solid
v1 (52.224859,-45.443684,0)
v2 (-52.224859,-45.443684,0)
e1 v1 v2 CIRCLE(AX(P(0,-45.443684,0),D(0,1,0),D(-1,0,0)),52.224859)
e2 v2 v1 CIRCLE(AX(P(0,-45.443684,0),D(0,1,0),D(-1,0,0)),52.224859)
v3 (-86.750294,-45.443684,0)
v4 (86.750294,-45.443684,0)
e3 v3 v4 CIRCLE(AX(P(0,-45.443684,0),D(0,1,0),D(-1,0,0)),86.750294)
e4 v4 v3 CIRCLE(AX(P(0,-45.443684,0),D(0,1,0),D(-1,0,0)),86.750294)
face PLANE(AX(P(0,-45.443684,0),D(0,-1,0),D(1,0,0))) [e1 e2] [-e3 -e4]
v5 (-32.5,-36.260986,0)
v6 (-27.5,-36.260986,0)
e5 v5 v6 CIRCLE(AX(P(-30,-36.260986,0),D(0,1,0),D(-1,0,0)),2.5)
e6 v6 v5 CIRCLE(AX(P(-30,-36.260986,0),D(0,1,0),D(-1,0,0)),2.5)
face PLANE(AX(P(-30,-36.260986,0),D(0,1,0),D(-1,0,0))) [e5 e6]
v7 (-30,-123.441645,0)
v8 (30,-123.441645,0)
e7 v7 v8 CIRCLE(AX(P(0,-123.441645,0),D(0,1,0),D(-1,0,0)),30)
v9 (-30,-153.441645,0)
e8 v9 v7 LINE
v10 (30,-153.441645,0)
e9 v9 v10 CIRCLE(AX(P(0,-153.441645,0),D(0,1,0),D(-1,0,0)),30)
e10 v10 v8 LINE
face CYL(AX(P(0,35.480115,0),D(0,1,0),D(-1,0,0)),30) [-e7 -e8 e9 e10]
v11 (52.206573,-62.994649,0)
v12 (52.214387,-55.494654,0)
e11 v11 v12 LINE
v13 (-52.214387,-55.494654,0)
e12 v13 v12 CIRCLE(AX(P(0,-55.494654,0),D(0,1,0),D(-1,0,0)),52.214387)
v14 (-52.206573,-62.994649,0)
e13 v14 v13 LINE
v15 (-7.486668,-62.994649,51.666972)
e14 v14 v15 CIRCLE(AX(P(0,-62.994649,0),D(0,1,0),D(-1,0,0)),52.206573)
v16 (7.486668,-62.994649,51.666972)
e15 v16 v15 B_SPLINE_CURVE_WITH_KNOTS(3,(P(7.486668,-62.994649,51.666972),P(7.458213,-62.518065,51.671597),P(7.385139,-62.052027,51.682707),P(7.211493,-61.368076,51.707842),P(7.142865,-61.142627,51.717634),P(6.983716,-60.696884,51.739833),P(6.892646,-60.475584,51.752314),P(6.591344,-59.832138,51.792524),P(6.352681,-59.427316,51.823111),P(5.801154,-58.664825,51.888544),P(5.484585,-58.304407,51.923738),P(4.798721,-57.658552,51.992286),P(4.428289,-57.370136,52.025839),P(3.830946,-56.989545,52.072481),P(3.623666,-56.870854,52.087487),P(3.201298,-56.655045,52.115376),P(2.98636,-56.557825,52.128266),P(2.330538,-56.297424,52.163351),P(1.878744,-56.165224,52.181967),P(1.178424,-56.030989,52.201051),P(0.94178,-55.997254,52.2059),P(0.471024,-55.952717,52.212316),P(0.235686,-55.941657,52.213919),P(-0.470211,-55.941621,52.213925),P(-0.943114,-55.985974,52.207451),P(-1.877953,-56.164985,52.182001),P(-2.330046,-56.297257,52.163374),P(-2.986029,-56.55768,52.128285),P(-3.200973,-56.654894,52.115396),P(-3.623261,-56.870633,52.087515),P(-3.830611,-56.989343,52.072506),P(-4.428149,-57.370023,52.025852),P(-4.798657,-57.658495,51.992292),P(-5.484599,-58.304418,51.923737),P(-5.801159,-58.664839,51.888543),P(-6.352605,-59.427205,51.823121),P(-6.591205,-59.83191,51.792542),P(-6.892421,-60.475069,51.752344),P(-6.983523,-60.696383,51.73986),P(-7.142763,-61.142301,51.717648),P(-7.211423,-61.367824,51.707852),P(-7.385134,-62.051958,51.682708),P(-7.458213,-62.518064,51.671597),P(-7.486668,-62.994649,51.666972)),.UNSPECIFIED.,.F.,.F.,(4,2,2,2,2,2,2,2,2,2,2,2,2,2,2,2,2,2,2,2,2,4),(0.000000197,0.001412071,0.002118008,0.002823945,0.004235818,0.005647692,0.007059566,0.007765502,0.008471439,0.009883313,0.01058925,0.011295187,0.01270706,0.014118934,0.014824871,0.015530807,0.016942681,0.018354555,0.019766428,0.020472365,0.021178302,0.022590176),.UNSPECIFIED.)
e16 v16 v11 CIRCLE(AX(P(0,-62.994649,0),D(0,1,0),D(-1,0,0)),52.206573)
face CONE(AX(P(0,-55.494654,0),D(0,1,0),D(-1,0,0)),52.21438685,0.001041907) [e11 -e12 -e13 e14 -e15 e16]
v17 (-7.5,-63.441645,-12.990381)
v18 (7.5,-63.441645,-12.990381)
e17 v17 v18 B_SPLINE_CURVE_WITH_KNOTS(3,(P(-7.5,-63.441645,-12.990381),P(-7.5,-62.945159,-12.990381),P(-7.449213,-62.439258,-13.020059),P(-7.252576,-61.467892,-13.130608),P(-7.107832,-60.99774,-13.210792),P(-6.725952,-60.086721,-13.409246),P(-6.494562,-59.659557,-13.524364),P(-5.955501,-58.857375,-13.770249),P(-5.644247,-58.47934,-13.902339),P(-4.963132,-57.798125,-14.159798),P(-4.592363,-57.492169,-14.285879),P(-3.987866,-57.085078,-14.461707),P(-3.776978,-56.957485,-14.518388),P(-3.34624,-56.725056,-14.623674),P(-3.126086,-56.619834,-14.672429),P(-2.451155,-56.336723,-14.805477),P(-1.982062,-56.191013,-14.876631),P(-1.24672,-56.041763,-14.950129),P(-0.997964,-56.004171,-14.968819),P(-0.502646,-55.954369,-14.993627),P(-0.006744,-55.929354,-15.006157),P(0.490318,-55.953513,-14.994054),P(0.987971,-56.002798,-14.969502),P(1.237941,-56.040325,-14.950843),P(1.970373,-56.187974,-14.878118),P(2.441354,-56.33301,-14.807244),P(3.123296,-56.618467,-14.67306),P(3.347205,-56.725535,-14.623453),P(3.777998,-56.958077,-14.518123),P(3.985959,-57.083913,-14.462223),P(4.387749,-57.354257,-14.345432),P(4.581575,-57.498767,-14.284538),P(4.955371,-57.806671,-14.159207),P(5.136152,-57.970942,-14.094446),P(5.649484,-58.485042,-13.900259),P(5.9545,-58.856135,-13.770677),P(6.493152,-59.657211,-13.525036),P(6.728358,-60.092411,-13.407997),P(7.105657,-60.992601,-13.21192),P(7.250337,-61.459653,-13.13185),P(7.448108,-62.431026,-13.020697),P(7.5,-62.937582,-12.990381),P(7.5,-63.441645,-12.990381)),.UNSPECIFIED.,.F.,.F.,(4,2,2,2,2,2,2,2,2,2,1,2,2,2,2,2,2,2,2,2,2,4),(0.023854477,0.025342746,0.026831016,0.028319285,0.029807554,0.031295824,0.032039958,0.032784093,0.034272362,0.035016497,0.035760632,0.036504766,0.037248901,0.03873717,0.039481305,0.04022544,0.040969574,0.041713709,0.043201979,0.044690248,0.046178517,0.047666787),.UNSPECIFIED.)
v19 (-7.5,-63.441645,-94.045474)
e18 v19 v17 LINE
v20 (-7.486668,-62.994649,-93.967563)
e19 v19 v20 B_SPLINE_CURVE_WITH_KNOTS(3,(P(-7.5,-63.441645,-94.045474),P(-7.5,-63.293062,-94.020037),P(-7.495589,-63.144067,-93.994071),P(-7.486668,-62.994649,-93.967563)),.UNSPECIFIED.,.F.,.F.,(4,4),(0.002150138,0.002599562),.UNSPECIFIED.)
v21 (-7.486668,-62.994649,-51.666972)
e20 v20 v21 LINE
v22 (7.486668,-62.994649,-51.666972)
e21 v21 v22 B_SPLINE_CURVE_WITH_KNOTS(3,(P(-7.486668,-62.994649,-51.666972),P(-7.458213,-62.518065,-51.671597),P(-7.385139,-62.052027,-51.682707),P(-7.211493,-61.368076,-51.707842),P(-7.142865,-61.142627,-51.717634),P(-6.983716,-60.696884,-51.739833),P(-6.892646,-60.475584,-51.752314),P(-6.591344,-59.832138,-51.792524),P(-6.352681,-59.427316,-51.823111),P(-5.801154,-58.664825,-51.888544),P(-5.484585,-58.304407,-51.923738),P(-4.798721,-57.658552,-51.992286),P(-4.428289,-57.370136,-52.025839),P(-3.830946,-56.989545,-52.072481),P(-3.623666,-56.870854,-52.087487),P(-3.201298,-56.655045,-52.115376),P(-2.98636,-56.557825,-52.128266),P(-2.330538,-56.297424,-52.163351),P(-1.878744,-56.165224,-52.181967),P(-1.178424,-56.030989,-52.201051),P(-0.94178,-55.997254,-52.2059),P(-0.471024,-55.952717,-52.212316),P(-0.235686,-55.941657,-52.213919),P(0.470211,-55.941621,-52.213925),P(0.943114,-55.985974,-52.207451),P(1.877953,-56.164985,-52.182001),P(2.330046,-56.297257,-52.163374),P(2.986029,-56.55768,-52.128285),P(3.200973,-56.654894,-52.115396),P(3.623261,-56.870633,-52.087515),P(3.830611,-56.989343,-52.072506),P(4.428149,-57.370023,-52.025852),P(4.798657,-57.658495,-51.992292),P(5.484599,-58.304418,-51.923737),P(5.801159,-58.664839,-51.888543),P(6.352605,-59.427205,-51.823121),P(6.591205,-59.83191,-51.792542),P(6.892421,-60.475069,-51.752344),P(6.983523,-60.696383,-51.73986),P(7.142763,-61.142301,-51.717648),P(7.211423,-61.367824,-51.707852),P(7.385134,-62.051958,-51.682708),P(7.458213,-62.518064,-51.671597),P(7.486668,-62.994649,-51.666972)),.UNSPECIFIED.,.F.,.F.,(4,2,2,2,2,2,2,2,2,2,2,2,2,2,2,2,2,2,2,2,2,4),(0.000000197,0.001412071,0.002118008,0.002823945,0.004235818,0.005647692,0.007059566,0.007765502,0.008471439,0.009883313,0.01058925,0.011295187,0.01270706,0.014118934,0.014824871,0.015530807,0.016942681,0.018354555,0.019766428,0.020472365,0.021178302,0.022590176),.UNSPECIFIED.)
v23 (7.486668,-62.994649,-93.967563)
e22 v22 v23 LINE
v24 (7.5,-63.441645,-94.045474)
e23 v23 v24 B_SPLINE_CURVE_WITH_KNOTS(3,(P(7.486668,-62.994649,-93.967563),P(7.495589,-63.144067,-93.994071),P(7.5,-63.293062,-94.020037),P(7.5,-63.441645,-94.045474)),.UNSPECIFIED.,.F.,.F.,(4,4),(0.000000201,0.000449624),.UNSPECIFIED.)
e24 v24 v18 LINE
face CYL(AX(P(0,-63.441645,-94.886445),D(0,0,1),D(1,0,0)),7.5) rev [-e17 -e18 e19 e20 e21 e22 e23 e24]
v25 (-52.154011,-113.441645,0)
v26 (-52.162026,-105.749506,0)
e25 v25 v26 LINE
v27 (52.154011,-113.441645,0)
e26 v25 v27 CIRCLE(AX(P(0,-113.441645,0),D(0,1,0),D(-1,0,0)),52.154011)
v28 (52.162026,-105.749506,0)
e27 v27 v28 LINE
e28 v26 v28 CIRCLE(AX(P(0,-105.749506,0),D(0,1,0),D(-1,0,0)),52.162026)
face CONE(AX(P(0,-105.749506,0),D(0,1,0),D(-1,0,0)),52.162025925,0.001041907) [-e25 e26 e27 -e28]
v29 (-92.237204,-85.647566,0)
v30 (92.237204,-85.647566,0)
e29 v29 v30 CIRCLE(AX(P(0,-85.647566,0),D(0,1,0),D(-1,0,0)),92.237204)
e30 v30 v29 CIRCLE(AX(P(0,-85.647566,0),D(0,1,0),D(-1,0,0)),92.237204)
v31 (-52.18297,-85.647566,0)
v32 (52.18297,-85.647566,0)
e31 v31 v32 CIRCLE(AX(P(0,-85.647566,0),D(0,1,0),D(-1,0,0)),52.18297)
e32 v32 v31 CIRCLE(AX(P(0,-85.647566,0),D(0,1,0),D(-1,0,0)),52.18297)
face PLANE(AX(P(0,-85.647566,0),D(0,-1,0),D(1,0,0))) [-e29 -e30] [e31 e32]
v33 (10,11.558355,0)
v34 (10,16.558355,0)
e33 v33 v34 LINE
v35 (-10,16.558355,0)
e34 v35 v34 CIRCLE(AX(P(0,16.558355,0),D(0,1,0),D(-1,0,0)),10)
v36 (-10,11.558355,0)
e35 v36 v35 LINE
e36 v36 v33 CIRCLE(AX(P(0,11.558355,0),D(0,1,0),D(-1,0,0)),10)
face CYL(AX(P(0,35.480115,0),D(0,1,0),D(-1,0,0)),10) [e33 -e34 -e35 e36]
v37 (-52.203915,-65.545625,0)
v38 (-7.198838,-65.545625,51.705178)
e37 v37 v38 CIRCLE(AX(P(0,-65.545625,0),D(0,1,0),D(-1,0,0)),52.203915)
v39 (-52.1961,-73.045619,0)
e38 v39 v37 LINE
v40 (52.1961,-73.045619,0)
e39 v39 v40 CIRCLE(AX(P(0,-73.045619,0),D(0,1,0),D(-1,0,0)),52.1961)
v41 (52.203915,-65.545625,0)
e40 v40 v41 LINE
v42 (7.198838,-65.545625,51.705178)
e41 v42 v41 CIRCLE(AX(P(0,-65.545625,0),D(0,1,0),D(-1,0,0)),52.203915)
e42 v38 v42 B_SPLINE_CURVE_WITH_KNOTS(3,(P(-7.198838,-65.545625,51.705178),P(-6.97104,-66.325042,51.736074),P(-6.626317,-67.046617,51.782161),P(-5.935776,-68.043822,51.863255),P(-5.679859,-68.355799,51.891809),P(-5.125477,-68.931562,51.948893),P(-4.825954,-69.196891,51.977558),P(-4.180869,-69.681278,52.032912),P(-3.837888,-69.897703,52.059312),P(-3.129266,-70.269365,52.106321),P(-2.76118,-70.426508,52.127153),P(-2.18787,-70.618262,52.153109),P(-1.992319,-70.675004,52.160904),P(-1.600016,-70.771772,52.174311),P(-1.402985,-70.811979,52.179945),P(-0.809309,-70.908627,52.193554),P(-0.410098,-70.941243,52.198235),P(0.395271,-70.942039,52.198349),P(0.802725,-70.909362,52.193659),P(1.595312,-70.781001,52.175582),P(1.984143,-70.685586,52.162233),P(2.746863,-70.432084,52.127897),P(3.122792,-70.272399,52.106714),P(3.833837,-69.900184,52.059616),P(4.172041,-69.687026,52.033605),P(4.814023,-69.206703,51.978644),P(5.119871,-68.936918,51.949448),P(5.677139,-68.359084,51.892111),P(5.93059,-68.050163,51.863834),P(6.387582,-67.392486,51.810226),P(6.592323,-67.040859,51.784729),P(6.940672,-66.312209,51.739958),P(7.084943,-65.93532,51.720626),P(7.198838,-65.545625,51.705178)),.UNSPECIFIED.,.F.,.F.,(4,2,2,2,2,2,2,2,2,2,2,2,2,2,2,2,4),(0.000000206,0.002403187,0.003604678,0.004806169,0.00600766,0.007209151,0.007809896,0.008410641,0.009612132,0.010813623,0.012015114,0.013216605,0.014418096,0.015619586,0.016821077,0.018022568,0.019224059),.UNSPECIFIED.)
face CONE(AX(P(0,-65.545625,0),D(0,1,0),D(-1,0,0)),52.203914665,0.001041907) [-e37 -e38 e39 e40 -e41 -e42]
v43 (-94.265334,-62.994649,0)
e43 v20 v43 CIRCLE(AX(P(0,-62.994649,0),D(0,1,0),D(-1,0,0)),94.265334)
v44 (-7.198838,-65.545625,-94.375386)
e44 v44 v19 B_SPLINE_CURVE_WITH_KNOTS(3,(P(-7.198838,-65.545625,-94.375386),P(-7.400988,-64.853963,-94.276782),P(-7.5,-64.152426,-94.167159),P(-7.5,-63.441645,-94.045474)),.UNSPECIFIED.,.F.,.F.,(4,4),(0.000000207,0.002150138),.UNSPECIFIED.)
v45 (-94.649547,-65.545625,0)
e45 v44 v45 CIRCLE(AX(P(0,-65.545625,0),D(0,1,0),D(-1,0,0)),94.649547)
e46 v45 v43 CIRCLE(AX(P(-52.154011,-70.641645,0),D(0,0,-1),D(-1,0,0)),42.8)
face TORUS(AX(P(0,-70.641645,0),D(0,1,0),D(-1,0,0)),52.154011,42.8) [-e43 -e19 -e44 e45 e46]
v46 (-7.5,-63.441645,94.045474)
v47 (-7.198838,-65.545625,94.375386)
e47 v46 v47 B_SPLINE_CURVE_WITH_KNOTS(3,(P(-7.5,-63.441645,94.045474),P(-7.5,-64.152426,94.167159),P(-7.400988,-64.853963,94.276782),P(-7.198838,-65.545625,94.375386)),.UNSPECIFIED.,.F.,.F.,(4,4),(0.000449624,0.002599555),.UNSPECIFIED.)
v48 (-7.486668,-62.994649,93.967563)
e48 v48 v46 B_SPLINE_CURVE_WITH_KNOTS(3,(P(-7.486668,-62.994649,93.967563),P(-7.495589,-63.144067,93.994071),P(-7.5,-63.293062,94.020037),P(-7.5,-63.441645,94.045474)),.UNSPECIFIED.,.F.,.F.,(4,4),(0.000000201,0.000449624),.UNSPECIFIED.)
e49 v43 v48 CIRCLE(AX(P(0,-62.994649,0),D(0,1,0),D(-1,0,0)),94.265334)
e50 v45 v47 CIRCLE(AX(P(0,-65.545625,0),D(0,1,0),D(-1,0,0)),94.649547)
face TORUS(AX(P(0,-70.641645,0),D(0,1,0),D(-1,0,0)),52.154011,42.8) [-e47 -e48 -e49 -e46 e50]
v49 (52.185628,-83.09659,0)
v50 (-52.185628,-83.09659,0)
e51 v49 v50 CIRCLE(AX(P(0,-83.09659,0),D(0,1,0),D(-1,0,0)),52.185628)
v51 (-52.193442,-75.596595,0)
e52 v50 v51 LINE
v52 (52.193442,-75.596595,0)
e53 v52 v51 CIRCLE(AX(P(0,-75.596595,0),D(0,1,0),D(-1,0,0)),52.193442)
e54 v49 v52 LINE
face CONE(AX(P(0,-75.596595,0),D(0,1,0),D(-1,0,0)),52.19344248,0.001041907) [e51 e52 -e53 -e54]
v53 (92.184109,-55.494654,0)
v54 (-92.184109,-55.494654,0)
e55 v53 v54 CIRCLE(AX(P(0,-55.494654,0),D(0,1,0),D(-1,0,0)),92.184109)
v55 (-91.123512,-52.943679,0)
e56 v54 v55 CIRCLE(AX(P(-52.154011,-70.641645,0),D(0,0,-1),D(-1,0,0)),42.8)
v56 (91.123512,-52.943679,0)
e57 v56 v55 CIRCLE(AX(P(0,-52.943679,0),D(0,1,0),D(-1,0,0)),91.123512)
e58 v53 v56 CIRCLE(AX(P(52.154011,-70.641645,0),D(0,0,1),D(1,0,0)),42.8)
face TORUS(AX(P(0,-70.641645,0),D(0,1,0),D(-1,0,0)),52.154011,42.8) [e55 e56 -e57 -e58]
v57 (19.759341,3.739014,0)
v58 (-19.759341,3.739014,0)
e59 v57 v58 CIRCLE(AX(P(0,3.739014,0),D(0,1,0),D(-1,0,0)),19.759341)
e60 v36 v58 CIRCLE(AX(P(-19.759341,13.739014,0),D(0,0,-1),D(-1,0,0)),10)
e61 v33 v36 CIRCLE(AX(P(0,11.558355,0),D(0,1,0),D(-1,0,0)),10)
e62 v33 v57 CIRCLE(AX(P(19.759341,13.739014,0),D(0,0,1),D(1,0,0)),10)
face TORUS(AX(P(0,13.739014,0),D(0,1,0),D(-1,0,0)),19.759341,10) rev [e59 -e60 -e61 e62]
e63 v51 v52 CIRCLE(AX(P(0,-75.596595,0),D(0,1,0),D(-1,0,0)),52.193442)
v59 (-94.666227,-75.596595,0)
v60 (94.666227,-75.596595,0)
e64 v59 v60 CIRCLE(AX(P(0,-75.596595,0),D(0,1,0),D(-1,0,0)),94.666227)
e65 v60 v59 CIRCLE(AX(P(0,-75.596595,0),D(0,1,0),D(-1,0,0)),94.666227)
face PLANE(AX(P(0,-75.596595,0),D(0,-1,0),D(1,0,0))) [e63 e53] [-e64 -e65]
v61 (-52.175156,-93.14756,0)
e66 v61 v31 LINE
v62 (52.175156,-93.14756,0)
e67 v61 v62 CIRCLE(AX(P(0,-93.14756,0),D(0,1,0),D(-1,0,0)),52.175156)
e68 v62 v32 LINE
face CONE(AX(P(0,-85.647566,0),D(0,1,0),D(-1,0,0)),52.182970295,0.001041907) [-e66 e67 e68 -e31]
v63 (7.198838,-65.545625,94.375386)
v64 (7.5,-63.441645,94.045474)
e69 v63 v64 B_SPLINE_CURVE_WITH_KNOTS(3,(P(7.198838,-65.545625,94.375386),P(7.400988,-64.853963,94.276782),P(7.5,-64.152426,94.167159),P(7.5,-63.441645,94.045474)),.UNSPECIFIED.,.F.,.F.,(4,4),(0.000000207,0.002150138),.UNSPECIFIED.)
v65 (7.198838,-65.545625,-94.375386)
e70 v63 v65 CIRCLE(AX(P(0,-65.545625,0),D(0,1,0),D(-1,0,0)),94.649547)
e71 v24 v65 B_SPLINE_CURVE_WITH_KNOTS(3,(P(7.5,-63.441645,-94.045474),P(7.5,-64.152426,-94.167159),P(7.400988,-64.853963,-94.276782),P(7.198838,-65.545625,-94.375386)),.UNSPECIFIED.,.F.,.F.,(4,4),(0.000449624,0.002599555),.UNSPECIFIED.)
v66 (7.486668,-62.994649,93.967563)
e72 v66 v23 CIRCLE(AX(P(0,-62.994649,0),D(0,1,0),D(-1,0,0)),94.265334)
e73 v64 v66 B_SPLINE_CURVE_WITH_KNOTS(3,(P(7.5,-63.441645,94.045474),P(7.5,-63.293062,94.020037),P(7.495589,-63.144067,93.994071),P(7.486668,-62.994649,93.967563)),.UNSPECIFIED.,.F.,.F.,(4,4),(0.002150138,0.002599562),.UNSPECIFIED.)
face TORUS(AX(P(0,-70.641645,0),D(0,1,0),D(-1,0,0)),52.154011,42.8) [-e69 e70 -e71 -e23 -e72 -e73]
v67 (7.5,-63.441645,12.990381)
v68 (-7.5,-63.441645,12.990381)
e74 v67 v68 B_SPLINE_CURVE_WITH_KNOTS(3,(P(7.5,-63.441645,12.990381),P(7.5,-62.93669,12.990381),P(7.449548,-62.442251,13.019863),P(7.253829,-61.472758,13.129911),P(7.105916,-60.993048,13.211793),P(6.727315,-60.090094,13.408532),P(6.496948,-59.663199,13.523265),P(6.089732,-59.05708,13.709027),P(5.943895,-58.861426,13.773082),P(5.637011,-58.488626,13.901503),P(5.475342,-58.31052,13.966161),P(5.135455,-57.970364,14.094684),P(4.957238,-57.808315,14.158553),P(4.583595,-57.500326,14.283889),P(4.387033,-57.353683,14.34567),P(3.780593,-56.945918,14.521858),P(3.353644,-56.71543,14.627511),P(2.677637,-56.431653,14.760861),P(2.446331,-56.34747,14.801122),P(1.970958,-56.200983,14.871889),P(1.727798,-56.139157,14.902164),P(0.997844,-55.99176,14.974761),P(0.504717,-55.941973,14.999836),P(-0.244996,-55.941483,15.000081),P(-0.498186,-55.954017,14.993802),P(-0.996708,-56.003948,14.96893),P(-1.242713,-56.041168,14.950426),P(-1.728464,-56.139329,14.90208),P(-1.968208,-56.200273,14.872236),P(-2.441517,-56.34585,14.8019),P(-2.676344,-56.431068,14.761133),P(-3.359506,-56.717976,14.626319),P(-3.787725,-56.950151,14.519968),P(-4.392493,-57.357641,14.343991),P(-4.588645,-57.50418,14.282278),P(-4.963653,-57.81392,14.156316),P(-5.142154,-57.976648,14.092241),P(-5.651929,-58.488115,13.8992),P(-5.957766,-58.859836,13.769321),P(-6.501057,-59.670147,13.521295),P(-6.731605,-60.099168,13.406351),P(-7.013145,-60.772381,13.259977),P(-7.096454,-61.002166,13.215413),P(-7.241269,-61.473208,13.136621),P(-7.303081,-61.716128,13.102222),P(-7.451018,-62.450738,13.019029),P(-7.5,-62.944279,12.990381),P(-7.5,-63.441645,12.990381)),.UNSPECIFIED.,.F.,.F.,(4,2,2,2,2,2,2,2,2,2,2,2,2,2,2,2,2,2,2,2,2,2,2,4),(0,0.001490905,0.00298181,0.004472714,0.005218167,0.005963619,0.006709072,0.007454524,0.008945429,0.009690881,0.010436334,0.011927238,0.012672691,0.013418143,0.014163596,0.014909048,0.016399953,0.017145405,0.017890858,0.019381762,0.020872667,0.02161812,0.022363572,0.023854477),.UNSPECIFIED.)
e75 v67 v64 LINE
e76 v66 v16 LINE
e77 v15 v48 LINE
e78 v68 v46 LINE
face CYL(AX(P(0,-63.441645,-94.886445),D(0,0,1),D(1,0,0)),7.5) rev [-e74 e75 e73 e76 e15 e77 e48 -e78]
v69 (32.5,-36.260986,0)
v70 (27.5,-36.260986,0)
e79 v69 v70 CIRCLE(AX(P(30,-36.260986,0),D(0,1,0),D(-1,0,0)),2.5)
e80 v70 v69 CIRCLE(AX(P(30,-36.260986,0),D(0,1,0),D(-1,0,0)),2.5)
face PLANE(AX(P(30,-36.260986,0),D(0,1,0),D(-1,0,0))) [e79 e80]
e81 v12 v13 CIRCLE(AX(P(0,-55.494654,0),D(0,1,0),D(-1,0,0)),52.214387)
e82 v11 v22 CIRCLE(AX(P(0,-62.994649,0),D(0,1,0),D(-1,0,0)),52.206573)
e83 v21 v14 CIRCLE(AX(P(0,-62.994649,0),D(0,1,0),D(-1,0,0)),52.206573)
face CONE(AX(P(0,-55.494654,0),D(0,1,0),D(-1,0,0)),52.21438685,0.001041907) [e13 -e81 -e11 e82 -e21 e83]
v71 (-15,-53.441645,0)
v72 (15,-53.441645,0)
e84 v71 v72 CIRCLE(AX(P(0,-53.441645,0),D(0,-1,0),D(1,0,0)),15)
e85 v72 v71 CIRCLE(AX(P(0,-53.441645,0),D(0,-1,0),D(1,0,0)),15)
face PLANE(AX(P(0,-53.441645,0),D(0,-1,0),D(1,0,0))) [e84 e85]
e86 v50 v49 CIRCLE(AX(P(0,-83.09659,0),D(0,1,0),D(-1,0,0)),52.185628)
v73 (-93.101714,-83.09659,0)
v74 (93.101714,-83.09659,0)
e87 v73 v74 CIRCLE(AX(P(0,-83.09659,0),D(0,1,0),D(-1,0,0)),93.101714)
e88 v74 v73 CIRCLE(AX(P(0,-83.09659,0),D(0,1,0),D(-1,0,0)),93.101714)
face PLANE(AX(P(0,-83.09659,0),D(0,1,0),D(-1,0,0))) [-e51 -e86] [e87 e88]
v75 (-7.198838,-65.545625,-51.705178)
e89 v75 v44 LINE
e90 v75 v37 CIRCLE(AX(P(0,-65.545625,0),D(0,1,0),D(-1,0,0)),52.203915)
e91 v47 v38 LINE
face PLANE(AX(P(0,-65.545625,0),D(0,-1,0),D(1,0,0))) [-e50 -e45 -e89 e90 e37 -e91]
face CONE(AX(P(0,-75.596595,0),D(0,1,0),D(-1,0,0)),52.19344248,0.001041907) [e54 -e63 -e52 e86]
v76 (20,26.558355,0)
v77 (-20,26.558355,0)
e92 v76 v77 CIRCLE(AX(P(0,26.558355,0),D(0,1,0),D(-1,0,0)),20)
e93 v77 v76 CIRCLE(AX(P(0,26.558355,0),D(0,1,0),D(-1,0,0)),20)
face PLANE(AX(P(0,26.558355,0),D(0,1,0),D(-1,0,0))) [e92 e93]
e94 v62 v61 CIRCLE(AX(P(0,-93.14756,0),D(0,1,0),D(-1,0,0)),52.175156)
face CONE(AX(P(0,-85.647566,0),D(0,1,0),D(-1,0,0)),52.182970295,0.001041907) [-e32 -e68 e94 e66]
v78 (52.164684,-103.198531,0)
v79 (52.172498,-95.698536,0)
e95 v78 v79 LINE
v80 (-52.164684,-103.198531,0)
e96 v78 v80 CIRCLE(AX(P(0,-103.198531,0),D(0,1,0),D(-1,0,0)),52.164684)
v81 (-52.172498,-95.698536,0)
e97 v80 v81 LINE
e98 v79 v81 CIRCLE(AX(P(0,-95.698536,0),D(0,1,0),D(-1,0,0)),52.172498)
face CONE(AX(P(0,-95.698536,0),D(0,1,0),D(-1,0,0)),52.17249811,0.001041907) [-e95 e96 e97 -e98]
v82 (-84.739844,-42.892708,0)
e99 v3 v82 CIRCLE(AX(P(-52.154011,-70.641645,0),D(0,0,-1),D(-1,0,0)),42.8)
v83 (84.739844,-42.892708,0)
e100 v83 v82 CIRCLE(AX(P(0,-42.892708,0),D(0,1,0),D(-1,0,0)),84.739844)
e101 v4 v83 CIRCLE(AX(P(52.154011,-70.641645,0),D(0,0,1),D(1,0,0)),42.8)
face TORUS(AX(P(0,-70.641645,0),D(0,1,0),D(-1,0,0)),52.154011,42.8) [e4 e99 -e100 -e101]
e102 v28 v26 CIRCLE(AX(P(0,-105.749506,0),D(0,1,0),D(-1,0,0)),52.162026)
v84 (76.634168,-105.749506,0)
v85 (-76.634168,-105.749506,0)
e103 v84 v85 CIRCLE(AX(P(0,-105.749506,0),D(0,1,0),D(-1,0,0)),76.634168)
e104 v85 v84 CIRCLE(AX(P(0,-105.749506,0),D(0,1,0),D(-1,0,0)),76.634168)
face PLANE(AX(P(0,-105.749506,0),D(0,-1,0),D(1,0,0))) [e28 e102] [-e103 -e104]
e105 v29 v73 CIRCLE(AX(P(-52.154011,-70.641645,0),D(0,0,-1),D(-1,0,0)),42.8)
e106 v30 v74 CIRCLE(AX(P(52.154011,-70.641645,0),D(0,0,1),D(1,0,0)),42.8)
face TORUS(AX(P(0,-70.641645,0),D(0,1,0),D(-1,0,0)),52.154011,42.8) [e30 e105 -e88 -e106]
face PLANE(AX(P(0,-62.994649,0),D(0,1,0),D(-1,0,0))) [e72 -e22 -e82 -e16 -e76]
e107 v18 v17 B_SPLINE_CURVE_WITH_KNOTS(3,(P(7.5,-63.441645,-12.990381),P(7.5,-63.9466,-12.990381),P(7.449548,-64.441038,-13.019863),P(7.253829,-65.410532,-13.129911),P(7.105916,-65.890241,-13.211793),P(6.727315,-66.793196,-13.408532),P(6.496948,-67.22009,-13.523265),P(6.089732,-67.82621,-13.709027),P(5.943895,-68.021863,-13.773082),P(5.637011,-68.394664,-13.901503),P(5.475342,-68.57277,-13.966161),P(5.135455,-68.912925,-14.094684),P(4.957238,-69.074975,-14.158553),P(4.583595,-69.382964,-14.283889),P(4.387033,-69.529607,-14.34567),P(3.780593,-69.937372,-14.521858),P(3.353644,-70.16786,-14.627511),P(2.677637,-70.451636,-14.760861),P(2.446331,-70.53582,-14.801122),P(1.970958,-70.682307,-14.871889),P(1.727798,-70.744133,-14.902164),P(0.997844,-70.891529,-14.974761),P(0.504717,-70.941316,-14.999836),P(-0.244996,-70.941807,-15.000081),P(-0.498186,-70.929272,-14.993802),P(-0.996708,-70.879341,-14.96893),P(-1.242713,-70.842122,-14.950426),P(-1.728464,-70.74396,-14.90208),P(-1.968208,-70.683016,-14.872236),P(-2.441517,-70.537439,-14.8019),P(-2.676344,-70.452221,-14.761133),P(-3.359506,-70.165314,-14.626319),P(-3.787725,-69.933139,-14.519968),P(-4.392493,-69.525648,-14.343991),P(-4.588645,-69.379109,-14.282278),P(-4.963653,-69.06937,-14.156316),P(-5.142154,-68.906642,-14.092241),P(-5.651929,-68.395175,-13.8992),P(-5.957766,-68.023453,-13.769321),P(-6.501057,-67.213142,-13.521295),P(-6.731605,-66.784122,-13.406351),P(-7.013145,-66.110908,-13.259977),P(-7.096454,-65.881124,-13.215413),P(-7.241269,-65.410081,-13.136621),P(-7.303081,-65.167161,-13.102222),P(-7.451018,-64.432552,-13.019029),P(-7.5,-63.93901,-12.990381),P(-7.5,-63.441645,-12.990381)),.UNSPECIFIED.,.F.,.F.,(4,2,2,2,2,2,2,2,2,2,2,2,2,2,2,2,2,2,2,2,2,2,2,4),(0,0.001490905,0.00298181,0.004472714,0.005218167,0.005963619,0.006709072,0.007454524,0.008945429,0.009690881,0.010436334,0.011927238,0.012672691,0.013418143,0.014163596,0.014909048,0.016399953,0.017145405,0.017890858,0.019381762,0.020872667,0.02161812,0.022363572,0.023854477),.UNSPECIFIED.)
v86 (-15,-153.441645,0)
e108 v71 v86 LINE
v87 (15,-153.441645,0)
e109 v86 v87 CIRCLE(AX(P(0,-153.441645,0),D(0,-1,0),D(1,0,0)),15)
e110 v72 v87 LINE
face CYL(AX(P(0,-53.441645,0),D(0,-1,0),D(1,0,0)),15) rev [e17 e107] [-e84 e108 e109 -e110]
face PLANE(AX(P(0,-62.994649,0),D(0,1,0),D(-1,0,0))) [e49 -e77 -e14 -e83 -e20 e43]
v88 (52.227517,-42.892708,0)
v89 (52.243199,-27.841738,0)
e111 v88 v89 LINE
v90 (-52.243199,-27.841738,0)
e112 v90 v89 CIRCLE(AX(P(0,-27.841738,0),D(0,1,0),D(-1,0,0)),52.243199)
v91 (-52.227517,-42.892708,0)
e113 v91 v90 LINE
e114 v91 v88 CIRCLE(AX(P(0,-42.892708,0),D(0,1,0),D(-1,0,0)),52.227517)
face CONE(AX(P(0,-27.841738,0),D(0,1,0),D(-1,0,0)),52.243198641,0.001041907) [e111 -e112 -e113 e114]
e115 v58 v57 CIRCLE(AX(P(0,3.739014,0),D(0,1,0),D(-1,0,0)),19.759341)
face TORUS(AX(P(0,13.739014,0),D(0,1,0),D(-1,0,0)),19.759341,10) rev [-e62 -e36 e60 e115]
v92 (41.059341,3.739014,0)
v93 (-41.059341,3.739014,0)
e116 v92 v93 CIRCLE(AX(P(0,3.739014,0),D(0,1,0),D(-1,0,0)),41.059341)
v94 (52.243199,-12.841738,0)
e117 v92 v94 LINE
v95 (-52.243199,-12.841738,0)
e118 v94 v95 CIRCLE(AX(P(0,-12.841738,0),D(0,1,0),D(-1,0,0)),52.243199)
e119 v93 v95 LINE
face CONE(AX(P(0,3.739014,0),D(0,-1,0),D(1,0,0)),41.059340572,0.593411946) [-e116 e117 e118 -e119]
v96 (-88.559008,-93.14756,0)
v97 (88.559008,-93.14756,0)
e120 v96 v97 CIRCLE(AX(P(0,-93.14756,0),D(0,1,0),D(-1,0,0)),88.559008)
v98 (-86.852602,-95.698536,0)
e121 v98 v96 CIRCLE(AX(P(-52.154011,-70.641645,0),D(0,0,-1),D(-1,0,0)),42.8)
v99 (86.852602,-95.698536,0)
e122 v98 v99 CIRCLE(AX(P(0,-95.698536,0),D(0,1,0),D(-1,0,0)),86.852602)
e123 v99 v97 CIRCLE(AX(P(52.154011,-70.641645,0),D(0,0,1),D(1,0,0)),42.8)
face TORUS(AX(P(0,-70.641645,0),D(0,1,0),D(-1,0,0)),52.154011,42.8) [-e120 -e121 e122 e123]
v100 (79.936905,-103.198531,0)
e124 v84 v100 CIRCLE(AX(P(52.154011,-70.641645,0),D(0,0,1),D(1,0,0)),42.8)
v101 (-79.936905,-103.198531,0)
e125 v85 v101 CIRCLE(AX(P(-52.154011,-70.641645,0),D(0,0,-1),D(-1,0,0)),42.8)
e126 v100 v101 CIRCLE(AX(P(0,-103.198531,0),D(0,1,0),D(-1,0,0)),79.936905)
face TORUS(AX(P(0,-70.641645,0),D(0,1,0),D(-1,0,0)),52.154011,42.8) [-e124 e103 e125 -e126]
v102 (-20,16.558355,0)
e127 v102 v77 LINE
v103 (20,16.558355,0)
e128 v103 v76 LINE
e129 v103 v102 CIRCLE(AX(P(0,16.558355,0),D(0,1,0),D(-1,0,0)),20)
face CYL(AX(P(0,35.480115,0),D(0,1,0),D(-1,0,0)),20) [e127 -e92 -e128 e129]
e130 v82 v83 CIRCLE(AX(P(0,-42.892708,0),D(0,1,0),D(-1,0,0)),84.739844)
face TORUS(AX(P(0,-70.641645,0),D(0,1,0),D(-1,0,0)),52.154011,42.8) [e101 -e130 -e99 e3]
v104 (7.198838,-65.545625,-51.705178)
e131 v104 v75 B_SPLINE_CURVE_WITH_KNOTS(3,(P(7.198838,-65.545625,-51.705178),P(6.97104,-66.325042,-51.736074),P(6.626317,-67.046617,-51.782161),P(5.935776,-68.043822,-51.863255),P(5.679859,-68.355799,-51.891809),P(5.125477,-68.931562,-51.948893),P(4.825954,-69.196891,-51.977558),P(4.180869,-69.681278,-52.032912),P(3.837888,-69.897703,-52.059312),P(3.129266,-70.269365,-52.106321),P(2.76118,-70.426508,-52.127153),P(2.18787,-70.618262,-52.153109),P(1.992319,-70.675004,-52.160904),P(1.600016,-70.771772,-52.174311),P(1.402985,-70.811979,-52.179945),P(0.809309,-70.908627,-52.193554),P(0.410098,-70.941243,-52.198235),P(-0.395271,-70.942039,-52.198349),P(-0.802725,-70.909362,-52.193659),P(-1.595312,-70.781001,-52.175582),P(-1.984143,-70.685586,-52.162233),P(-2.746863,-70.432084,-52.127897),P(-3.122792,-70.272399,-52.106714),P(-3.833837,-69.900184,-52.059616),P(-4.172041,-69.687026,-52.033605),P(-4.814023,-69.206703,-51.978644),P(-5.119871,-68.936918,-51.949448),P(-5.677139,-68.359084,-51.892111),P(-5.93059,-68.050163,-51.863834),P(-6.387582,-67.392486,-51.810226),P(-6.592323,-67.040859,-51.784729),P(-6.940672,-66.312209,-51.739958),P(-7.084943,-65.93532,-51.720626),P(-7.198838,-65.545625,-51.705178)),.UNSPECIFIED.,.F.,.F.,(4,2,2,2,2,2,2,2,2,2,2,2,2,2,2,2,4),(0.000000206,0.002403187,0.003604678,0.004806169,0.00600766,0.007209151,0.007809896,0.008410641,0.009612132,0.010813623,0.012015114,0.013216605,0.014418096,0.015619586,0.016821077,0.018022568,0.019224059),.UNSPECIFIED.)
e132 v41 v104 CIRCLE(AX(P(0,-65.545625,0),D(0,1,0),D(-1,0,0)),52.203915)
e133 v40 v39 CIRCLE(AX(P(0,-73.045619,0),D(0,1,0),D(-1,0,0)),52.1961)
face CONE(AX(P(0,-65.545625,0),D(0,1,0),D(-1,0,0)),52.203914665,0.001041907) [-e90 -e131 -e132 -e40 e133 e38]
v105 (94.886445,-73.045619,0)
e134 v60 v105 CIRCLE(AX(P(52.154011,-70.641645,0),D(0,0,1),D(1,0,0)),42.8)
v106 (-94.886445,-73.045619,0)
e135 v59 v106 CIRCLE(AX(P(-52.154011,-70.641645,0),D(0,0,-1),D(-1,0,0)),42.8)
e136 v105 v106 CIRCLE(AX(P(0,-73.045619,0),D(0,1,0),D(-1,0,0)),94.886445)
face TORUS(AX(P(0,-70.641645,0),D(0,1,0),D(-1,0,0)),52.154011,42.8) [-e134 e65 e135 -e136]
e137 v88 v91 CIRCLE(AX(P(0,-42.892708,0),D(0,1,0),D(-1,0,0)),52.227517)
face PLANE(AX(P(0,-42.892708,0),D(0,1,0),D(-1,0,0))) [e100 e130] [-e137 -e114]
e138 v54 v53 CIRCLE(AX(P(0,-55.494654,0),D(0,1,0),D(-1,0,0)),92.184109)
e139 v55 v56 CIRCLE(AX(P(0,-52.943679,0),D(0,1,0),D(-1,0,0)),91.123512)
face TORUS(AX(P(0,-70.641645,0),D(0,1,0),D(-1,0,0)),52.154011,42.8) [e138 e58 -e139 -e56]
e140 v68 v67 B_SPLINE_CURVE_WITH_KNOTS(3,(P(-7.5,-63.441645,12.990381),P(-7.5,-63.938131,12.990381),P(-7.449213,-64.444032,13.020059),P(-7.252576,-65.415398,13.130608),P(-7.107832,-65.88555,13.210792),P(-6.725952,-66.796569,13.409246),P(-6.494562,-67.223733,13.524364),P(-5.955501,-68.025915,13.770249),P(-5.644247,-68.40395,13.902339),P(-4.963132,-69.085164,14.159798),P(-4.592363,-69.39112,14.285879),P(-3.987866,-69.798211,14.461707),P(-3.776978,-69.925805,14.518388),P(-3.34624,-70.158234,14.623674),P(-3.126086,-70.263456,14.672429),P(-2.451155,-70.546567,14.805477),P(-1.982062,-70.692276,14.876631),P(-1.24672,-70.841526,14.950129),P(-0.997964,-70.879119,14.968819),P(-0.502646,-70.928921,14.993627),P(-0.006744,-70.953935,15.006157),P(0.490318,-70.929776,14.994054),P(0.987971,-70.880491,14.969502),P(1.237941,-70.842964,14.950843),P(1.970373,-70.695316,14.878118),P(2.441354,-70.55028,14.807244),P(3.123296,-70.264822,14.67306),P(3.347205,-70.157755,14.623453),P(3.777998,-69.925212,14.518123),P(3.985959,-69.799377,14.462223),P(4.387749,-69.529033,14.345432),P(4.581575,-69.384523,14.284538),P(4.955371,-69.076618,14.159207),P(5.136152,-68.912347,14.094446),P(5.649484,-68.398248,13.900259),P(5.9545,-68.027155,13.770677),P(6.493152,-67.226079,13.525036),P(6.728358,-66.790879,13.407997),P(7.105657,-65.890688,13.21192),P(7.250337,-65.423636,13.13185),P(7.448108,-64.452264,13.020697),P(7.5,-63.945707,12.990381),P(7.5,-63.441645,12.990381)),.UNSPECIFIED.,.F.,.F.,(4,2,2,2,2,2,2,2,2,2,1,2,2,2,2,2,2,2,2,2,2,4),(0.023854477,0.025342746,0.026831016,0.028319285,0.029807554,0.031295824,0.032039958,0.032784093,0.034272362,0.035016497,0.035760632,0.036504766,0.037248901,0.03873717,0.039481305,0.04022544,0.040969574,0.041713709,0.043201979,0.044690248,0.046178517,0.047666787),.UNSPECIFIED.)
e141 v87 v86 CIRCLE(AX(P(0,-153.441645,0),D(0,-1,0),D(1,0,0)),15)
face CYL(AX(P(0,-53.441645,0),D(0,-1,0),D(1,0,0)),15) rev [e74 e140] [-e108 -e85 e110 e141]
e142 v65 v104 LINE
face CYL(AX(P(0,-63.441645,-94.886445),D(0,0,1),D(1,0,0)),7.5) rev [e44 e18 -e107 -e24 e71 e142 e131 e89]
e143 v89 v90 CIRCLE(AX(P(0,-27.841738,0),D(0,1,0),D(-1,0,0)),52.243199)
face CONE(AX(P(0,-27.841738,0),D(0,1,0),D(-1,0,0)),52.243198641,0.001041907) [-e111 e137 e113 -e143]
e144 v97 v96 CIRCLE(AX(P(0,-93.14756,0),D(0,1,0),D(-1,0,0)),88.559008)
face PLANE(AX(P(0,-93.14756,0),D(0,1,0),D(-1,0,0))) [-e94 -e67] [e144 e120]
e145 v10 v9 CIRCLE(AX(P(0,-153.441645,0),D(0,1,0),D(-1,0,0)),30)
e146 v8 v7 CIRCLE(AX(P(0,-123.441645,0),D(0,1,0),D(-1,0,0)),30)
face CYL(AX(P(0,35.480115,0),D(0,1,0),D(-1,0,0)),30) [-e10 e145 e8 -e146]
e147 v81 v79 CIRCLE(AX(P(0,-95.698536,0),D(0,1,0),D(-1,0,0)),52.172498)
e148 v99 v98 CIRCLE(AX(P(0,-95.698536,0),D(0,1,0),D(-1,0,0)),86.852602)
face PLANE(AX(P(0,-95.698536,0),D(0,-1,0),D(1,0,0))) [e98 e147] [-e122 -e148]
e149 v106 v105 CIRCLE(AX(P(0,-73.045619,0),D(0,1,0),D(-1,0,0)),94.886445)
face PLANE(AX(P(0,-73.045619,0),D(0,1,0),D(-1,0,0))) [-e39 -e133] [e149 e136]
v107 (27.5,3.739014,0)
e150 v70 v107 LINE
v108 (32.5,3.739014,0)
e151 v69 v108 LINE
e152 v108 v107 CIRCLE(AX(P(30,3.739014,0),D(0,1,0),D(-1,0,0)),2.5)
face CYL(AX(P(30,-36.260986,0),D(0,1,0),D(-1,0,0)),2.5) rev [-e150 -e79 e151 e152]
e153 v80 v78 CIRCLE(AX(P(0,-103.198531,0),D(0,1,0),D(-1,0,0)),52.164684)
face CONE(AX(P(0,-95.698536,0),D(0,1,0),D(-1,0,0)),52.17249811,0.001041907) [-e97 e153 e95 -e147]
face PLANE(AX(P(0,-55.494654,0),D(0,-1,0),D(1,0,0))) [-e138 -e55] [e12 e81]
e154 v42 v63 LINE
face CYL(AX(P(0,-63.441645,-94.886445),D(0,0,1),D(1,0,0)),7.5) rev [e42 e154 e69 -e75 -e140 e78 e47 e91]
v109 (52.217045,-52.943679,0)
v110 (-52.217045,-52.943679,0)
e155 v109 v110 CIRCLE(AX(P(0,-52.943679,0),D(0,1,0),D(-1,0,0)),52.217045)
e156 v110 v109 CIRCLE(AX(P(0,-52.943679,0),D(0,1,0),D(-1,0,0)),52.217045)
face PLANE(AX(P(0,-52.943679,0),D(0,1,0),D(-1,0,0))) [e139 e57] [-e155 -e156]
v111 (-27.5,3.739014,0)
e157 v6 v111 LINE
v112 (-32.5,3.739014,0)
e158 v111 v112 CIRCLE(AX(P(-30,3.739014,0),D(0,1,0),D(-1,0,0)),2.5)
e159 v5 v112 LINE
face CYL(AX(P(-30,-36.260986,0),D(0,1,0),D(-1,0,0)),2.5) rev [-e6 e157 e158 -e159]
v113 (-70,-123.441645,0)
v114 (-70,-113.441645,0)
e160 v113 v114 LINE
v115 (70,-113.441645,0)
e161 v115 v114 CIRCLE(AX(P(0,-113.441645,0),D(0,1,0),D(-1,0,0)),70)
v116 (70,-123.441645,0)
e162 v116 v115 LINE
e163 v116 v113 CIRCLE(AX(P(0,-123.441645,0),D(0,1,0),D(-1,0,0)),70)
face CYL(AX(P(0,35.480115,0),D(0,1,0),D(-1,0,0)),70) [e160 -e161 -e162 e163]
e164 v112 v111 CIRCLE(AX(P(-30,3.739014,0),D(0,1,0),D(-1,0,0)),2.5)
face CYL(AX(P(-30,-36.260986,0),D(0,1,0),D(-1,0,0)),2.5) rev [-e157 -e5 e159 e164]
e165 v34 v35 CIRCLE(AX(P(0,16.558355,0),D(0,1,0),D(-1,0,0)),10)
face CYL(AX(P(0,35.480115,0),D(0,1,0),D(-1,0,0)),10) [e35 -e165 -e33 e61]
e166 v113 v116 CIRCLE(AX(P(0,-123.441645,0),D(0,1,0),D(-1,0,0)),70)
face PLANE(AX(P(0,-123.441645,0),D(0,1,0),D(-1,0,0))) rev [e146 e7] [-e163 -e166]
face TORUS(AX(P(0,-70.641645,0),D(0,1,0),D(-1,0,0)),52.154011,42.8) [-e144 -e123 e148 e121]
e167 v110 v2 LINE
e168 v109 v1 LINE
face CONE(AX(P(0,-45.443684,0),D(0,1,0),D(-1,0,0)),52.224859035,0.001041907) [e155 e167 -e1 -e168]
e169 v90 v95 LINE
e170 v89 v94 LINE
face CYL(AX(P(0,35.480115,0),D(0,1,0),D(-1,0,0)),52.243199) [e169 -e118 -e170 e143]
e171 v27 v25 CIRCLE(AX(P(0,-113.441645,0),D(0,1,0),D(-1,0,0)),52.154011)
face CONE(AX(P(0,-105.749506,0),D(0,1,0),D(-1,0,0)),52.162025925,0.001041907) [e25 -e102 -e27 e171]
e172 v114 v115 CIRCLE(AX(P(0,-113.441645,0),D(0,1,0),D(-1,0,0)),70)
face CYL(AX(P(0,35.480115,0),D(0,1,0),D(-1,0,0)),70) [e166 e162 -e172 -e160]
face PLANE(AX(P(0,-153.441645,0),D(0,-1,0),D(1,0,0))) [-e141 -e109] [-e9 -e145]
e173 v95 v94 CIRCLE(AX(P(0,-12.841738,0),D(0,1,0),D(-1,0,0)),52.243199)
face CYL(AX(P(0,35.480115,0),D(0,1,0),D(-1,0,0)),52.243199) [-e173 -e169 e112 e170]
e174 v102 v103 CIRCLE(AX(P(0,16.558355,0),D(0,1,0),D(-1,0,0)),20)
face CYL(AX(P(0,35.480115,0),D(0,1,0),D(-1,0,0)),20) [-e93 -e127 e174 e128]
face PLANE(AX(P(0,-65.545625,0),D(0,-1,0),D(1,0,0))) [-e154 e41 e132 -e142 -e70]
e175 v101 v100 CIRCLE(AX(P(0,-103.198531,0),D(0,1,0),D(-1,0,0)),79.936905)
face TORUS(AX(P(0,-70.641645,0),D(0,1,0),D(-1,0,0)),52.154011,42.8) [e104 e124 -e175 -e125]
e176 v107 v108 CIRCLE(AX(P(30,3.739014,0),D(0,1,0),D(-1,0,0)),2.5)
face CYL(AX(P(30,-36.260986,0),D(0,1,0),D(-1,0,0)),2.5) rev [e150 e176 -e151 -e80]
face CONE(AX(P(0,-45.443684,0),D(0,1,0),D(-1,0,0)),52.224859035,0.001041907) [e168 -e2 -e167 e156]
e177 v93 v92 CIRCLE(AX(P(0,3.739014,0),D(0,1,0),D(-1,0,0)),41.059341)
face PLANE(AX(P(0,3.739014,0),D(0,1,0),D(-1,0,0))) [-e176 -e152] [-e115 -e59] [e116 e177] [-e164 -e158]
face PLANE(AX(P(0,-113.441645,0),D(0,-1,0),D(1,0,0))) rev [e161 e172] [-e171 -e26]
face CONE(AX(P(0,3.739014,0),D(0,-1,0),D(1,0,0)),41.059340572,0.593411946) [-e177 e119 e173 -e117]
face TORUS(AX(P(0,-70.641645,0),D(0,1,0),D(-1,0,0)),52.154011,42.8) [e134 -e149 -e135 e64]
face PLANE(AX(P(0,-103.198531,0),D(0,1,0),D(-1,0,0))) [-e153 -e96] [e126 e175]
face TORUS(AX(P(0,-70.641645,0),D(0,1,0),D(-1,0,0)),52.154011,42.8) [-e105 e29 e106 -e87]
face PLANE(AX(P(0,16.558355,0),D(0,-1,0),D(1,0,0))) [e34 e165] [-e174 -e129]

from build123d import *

# Parameters (mm, degrees)
CUT_30_SKETCH_R               = 15
CUT_30_DEPTH                  = 100
RECTANGULAR_CUT_SKETCH_R      = 2.5
RECTANGULAR_CUT_40_DEEP_DEPTH = 40
FRONT_PLANE_CUT_DEPTH         = 204.841147396
FRONT_PLANE_CUT_DEPTH_BACK    = 204.841147396
FRONT_PLANE_CUT_SKETCH_R      = 7.5


with BuildPart() as part:
    # Turned Body Profile → Turned Body (revolve)
    with BuildSketch(Plane.XY, mode=Mode.PRIVATE) as turned_body_sk:
        with BuildLine():
            Line((20, 26.558355194), (0, 26.558355194))
            Line((0, 26.558355194), (0, -153.441644806))
            Line((0, -153.441644806), (30, -153.441644806))
            Line((30, -153.441644806), (30, -123.441644806))
            Line((30, -123.441644806), (70, -123.441644806))
            Line((70, -123.441644806), (70, -113.441644806))
            Line((70, -113.441644806), (52.154011426, -113.441644806))
            Line((52.154011426, -113.441644806), (52.162025925, -105.749506337))
            Line((52.162025925, -105.749506337), (76.634167854, -105.749506337))
            ThreePointArc((76.634167854, -105.749506337), (78.316646551, -104.51429636), (79.93690532, -103.198530512))
            Line((79.93690532, -103.198530512), (52.164683807, -103.198530512))
            Line((52.164683807, -103.198530512), (52.17249811, -95.698535939))
            Line((52.17249811, -95.698535939), (86.852602272, -95.698535939))
            ThreePointArc((86.852602272, -95.698535939), (87.728678054, -94.438348239), (88.559008008, -93.147560114))
            Line((88.559008008, -93.147560114), (52.175155992, -93.147560114))
            Line((52.175155992, -93.147560114), (52.182970295, -85.647565542))
            Line((52.182970295, -85.647565542), (92.237204199, -85.647565542))
            ThreePointArc((92.237204199, -85.647565542), (92.689531284, -84.378879966), (93.101714014, -83.096589717))
            Line((93.101714014, -83.096589717), (52.185628177, -83.096589717))
            Line((52.185628177, -83.096589717), (52.19344248, -75.596595145))
            Line((52.19344248, -75.596595145), (94.666226931, -75.596595145))
            ThreePointArc((94.666226931, -75.596595145), (94.795416565, -74.322754392), (94.88644532, -73.04561932))
            Line((94.88644532, -73.04561932), (52.196100362, -73.04561932))
            Line((52.196100362, -73.04561932), (52.203914665, -65.545624748))
            Line((52.203914665, -65.545624748), (94.649547422, -65.545624748))
            ThreePointArc((94.649547422, -65.545624748), (94.476664711, -64.267241391), (94.265333585, -62.994648923))
            Line((94.265333585, -62.994648923), (52.206572547, -62.994648923))
            Line((52.206572547, -62.994648923), (52.21438685, -55.49465435))
            Line((52.21438685, -55.49465435), (92.184108605, -55.49465435))
            ThreePointArc((92.184108605, -55.49465435), (91.674398419, -54.210606739), (91.123512187, -52.943678525))
            Line((91.123512187, -52.943678525), (52.217044732, -52.943678525))
            Line((52.217044732, -52.943678525), (52.224859035, -45.443683953))
            Line((52.224859035, -45.443683953), (86.750294013, -45.443683953))
            ThreePointArc((86.750294013, -45.443683953), (85.769276316, -44.149118192), (84.73984444, -42.892708128))
            Line((84.73984444, -42.892708128), (52.227516917, -42.892708128))
            Line((52.227516917, -42.892708128), (52.23533122, -35.392713556))
            Line((52.23533122, -35.392713556), (52.237989102, -32.841737731))
            Line((52.237989102, -32.841737731), (52.243198641, -27.841737731))
            Line((52.243198641, -27.841737731), (52.243198641, -12.841737731))
            Line((52.243198641, -12.841737731), (41.059340572, 3.73901372))
            Line((41.059340572, 3.73901372), (19.759340572, 3.73901372))
            ThreePointArc((19.759340572, 3.73901372), (13.506604581, 5.934957555), (10, 11.558355194))
            Line((10, 11.558355194), (10, 16.558355194))
            Line((10, 16.558355194), (20, 16.558355194))
            Line((20, 16.558355194), (20, 26.558355194))
        make_face()
    revolve(turned_body_sk.sketch.rotate(Axis((0, 35.480114724, 0), (0, -1, 0)), 180), axis=Axis((0, 35.480114724, 0), (0, -1, 0)))

    # Cut Ø30 Sketch → Cut Ø30 (cut)
    with BuildSketch(Plane.XZ.offset(153.441644806)):
        Circle(CUT_30_SKETCH_R)
    extrude(amount=-CUT_30_DEPTH, mode=Mode.SUBTRACT)

    # Rectangular Cut Sketch → Rectangular Cut 40 Deep (cut)
    with BuildSketch(Plane(origin=(0, 3.73901372, 0), x_dir=(1, 0, 0), z_dir=(0, 1, 0))):
        with Locations(Location((30, 0, 0), (0, 0, 180))):
            Circle(RECTANGULAR_CUT_SKETCH_R)
        with Locations(Location((-30, 0, 0), (0, 0, 180))):
            Circle(RECTANGULAR_CUT_SKETCH_R)
    extrude(amount=-RECTANGULAR_CUT_40_DEEP_DEPTH, mode=Mode.SUBTRACT)

    # Front Plane Cut Sketch → Front Plane Cut (cut, two sides: drawn at the far end of the back side and taken through both)
    with BuildSketch(Plane.XY.offset(-FRONT_PLANE_CUT_DEPTH_BACK)):
        with Locations((0, -63.441644806)):
            Circle(FRONT_PLANE_CUT_SKETCH_R)
    extrude(amount=FRONT_PLANE_CUT_DEPTH + FRONT_PLANE_CUT_DEPTH_BACK, mode=Mode.SUBTRACT)


solid = part.part
